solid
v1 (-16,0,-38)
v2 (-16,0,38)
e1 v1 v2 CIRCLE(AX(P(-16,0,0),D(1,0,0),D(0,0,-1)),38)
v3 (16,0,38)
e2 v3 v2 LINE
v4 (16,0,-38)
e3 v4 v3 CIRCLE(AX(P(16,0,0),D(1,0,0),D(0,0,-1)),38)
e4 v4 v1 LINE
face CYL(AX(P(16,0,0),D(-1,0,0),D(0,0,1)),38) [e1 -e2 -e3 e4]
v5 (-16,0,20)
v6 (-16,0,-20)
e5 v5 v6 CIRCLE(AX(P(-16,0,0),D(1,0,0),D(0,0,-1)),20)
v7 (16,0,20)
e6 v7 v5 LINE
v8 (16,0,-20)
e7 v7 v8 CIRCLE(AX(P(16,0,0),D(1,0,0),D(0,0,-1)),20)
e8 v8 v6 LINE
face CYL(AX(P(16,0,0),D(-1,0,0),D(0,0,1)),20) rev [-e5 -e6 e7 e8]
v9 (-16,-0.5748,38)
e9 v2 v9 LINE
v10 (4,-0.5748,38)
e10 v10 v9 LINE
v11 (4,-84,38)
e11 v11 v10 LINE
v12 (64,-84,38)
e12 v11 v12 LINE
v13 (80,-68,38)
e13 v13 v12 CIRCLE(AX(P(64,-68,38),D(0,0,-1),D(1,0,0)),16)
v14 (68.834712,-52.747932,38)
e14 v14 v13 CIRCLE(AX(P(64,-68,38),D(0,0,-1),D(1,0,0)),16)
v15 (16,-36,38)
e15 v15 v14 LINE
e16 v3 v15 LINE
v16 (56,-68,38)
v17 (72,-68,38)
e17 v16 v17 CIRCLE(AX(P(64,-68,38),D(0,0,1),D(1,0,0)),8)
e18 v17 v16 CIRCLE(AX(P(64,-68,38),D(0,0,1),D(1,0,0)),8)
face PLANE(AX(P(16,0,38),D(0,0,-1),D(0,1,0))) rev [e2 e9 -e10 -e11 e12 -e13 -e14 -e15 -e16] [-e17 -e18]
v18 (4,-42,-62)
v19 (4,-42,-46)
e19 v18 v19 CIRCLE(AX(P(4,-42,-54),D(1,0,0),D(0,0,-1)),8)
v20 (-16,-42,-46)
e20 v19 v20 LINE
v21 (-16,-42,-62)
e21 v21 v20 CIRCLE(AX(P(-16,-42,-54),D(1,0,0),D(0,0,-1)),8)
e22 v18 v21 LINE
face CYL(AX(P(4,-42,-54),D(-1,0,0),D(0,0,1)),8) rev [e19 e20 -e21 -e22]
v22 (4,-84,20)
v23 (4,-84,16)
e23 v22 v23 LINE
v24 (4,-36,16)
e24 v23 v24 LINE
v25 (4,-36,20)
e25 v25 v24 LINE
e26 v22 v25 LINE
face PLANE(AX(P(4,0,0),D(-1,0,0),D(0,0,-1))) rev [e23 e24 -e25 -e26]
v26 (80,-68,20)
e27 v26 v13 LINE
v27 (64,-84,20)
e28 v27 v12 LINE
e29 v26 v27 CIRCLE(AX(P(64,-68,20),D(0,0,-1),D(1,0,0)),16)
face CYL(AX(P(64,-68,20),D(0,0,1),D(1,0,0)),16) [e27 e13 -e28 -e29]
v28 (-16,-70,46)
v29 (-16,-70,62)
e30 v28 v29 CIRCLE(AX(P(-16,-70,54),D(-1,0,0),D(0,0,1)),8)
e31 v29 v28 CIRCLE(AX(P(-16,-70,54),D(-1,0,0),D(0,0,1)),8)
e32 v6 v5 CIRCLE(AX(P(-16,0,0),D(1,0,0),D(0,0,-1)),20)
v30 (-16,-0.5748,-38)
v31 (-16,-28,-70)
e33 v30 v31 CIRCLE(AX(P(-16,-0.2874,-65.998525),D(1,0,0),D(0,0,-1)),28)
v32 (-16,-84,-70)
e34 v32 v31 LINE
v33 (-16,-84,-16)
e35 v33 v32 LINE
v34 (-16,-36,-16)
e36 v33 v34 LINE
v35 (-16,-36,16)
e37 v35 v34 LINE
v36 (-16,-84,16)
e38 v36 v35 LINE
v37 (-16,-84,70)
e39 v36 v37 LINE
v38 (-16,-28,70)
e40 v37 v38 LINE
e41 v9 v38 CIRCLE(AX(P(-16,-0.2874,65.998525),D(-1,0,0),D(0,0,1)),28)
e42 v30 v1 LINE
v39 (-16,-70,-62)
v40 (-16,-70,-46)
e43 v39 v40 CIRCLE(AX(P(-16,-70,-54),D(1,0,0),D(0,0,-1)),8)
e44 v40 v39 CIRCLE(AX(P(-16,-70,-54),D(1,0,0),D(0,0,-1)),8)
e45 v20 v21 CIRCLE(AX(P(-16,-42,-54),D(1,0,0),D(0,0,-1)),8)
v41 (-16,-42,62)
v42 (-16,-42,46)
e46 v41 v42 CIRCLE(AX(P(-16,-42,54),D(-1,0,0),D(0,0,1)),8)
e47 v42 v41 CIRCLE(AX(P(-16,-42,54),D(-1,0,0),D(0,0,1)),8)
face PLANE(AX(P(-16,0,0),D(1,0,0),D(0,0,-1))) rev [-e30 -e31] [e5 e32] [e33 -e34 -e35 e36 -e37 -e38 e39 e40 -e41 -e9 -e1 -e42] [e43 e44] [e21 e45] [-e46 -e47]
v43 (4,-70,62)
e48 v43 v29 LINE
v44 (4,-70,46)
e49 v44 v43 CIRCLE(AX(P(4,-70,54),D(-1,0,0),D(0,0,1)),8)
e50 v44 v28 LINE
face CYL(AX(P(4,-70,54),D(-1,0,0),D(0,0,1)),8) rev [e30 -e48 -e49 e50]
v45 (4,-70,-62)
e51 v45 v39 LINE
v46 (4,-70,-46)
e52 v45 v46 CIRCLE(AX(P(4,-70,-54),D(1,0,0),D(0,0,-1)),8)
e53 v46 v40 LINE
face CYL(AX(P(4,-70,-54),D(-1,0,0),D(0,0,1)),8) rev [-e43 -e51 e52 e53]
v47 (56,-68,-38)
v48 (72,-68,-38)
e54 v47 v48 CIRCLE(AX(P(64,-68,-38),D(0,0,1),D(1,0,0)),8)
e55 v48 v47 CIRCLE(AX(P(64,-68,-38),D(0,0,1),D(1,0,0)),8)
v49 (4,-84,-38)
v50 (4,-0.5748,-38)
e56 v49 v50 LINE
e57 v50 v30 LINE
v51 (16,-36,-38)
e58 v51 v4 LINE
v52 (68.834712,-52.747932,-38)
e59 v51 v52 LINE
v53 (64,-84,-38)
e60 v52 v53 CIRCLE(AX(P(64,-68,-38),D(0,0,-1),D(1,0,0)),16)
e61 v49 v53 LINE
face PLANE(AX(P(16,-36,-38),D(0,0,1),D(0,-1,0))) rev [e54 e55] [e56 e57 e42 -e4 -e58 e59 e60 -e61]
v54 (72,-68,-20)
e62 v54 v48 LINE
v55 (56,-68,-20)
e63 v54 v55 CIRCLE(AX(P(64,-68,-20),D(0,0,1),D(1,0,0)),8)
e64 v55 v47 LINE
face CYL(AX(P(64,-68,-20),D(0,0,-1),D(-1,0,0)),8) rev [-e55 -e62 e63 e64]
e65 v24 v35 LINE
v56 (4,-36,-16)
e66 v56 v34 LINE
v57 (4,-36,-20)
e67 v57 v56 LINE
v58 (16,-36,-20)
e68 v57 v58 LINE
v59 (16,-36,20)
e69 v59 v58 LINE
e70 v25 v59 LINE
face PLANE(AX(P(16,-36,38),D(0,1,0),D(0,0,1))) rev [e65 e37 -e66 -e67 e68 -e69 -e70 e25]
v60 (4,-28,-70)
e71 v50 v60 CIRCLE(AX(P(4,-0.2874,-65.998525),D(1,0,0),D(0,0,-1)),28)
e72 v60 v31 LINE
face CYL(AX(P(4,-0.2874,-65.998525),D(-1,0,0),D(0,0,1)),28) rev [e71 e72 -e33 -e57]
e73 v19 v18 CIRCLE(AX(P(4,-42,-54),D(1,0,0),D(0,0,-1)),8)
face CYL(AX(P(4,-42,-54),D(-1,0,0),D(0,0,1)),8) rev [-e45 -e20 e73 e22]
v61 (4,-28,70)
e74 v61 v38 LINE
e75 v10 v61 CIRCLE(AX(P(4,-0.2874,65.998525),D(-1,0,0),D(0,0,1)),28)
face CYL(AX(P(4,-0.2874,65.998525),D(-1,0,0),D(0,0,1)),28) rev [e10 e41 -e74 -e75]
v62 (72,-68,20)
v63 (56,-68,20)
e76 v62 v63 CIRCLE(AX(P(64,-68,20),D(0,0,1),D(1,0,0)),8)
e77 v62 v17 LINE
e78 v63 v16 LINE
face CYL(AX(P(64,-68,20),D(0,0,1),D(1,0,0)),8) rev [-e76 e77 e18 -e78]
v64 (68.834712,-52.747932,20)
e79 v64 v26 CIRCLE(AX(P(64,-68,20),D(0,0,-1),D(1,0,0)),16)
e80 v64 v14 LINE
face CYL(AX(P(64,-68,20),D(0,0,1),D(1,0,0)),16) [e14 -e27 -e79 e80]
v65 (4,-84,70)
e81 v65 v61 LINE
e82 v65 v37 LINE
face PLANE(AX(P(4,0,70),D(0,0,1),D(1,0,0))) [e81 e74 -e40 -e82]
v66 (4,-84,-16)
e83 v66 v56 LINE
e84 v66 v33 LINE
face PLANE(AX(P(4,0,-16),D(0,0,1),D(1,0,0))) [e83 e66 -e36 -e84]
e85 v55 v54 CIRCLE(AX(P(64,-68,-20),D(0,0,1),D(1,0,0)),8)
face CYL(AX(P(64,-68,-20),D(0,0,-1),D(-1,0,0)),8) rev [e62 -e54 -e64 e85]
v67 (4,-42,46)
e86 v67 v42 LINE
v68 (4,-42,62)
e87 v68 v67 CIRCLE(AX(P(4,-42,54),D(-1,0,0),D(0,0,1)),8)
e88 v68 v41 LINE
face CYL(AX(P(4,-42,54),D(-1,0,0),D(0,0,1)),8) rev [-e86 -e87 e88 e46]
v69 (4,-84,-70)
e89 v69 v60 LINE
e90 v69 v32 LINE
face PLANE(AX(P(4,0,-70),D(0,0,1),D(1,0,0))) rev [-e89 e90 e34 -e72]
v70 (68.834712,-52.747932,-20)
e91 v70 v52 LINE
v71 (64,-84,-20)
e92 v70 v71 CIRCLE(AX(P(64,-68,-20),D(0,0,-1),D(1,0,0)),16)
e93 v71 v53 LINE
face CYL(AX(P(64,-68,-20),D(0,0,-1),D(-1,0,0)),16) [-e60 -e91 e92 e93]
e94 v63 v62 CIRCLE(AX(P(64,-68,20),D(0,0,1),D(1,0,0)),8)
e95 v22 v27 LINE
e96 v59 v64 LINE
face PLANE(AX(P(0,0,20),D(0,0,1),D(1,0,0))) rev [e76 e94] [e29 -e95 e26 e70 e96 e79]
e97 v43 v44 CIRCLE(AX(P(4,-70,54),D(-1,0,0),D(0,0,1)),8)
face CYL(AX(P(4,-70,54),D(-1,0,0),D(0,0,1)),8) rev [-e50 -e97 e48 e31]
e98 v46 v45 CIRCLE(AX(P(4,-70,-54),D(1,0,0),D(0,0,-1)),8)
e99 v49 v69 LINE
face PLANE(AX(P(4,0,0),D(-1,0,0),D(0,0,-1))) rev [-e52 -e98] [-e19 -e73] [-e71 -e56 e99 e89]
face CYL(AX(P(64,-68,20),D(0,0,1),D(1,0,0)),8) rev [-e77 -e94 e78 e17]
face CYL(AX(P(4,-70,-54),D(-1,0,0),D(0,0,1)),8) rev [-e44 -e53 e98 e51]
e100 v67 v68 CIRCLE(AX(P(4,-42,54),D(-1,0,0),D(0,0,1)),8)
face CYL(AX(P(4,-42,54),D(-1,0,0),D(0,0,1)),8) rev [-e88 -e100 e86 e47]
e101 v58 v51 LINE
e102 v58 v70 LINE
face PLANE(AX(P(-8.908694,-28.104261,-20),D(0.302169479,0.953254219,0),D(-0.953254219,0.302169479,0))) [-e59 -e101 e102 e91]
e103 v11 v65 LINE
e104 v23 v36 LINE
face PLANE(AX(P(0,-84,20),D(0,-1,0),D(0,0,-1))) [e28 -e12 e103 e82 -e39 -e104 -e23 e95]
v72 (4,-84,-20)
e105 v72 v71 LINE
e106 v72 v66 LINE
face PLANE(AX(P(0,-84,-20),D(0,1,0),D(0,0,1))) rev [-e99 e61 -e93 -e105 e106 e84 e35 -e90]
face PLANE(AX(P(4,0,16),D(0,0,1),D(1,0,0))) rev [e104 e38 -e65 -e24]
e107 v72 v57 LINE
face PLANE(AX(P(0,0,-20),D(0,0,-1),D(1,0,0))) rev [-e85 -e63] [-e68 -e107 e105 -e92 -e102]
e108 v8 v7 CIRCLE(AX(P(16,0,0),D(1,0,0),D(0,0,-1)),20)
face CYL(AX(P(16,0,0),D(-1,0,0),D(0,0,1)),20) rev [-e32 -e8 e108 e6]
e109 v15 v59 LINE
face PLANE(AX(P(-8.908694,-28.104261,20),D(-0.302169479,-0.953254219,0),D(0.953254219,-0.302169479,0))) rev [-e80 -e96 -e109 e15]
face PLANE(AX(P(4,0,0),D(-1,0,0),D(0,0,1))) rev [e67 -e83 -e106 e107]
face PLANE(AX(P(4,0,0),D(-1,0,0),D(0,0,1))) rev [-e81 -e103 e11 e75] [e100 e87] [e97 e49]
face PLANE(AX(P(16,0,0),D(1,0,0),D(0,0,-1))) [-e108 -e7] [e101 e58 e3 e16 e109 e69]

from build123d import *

# Parameters (mm, degrees)
HUB_PROFILE_SKETCH_R    = 20
HUB_BOSS_DEPTH          = 16
ARM_PROFILE_SKETCH_R    = 8
ARM_BOSS_DEPTH          = 18
FLANGE_PROFILE_SKETCH_R = 8
FLANGE_BOSS_DEPTH       = 20
WEB_PROFILE_SKETCH_W    = 4
WEB_PROFILE_SKETCH_H    = 48
WEB_BOSS_DEPTH          = 20


with BuildPart() as part:
    # Hub Profile Sketch → Hub Boss (new, symmetric)
    with BuildSketch(Plane(origin=(0, 0, 0), x_dir=(0, 0, -1), z_dir=(1, 0, 0))):
        with BuildLine():
            Line((-38, 0), (-38, -36))
            Line((-38, -36), (38, -36))
            Line((38, -36), (38, 0))
            ThreePointArc((38, 0), (0, 38), (-38, 0))
        make_face()
        Circle(HUB_PROFILE_SKETCH_R, mode=Mode.SUBTRACT)
    extrude(amount=HUB_BOSS_DEPTH, both=True)

    # Arm Profile Sketch → Arm Boss (add)
    with BuildSketch(Plane.XY.offset(38)):
        with BuildLine():
            ThreePointArc((68.834711668, -52.747932498), (79.811911333, -70.446111196), (64, -84))
            Line((64, -84), (-16, -84))
            Line((-16, -84), (-16, -36))
            Line((-16, -36), (16, -36))
            Line((16, -36), (68.834711668, -52.747932498))
        make_face()
        with Locations((64, -68)):
            Circle(ARM_PROFILE_SKETCH_R, mode=Mode.SUBTRACT)
    arm_boss = extrude(amount=-ARM_BOSS_DEPTH)

    # Arm Mirror: Arm Boss across plane
    add(arm_boss.mirror(Plane.XY))

    # Flange Profile Sketch → Flange Boss (add)
    with BuildSketch(Plane.ZY.offset(16)):
        with BuildLine():
            ThreePointArc((70, -28), (47.777657825, -21.547691645), (38, -0.574800039))
            Line((38, -0.574800039), (38, -84))
            Line((38, -84), (70, -84))
            Line((70, -84), (70, -28))
        make_face()
        with Locations((54, -70)):
            Circle(FLANGE_PROFILE_SKETCH_R, mode=Mode.SUBTRACT)
        with Locations((54, -42)):
            Circle(FLANGE_PROFILE_SKETCH_R, mode=Mode.SUBTRACT)
    flange_boss = extrude(amount=-FLANGE_BOSS_DEPTH)

    # Flange Mirror: Flange Boss across plane
    add(flange_boss.mirror(Plane.XY))

    # Web Profile Sketch → Web Boss (add)
    with BuildSketch(Plane.ZY.offset(16)):
        with Locations((-18, -60)):
            Rectangle(WEB_PROFILE_SKETCH_W, WEB_PROFILE_SKETCH_H)
    web_boss = extrude(amount=-WEB_BOSS_DEPTH)

    # Web Mirror: Web Boss across plane
    add(web_boss.mirror(Plane.XY))


solid = part.part
